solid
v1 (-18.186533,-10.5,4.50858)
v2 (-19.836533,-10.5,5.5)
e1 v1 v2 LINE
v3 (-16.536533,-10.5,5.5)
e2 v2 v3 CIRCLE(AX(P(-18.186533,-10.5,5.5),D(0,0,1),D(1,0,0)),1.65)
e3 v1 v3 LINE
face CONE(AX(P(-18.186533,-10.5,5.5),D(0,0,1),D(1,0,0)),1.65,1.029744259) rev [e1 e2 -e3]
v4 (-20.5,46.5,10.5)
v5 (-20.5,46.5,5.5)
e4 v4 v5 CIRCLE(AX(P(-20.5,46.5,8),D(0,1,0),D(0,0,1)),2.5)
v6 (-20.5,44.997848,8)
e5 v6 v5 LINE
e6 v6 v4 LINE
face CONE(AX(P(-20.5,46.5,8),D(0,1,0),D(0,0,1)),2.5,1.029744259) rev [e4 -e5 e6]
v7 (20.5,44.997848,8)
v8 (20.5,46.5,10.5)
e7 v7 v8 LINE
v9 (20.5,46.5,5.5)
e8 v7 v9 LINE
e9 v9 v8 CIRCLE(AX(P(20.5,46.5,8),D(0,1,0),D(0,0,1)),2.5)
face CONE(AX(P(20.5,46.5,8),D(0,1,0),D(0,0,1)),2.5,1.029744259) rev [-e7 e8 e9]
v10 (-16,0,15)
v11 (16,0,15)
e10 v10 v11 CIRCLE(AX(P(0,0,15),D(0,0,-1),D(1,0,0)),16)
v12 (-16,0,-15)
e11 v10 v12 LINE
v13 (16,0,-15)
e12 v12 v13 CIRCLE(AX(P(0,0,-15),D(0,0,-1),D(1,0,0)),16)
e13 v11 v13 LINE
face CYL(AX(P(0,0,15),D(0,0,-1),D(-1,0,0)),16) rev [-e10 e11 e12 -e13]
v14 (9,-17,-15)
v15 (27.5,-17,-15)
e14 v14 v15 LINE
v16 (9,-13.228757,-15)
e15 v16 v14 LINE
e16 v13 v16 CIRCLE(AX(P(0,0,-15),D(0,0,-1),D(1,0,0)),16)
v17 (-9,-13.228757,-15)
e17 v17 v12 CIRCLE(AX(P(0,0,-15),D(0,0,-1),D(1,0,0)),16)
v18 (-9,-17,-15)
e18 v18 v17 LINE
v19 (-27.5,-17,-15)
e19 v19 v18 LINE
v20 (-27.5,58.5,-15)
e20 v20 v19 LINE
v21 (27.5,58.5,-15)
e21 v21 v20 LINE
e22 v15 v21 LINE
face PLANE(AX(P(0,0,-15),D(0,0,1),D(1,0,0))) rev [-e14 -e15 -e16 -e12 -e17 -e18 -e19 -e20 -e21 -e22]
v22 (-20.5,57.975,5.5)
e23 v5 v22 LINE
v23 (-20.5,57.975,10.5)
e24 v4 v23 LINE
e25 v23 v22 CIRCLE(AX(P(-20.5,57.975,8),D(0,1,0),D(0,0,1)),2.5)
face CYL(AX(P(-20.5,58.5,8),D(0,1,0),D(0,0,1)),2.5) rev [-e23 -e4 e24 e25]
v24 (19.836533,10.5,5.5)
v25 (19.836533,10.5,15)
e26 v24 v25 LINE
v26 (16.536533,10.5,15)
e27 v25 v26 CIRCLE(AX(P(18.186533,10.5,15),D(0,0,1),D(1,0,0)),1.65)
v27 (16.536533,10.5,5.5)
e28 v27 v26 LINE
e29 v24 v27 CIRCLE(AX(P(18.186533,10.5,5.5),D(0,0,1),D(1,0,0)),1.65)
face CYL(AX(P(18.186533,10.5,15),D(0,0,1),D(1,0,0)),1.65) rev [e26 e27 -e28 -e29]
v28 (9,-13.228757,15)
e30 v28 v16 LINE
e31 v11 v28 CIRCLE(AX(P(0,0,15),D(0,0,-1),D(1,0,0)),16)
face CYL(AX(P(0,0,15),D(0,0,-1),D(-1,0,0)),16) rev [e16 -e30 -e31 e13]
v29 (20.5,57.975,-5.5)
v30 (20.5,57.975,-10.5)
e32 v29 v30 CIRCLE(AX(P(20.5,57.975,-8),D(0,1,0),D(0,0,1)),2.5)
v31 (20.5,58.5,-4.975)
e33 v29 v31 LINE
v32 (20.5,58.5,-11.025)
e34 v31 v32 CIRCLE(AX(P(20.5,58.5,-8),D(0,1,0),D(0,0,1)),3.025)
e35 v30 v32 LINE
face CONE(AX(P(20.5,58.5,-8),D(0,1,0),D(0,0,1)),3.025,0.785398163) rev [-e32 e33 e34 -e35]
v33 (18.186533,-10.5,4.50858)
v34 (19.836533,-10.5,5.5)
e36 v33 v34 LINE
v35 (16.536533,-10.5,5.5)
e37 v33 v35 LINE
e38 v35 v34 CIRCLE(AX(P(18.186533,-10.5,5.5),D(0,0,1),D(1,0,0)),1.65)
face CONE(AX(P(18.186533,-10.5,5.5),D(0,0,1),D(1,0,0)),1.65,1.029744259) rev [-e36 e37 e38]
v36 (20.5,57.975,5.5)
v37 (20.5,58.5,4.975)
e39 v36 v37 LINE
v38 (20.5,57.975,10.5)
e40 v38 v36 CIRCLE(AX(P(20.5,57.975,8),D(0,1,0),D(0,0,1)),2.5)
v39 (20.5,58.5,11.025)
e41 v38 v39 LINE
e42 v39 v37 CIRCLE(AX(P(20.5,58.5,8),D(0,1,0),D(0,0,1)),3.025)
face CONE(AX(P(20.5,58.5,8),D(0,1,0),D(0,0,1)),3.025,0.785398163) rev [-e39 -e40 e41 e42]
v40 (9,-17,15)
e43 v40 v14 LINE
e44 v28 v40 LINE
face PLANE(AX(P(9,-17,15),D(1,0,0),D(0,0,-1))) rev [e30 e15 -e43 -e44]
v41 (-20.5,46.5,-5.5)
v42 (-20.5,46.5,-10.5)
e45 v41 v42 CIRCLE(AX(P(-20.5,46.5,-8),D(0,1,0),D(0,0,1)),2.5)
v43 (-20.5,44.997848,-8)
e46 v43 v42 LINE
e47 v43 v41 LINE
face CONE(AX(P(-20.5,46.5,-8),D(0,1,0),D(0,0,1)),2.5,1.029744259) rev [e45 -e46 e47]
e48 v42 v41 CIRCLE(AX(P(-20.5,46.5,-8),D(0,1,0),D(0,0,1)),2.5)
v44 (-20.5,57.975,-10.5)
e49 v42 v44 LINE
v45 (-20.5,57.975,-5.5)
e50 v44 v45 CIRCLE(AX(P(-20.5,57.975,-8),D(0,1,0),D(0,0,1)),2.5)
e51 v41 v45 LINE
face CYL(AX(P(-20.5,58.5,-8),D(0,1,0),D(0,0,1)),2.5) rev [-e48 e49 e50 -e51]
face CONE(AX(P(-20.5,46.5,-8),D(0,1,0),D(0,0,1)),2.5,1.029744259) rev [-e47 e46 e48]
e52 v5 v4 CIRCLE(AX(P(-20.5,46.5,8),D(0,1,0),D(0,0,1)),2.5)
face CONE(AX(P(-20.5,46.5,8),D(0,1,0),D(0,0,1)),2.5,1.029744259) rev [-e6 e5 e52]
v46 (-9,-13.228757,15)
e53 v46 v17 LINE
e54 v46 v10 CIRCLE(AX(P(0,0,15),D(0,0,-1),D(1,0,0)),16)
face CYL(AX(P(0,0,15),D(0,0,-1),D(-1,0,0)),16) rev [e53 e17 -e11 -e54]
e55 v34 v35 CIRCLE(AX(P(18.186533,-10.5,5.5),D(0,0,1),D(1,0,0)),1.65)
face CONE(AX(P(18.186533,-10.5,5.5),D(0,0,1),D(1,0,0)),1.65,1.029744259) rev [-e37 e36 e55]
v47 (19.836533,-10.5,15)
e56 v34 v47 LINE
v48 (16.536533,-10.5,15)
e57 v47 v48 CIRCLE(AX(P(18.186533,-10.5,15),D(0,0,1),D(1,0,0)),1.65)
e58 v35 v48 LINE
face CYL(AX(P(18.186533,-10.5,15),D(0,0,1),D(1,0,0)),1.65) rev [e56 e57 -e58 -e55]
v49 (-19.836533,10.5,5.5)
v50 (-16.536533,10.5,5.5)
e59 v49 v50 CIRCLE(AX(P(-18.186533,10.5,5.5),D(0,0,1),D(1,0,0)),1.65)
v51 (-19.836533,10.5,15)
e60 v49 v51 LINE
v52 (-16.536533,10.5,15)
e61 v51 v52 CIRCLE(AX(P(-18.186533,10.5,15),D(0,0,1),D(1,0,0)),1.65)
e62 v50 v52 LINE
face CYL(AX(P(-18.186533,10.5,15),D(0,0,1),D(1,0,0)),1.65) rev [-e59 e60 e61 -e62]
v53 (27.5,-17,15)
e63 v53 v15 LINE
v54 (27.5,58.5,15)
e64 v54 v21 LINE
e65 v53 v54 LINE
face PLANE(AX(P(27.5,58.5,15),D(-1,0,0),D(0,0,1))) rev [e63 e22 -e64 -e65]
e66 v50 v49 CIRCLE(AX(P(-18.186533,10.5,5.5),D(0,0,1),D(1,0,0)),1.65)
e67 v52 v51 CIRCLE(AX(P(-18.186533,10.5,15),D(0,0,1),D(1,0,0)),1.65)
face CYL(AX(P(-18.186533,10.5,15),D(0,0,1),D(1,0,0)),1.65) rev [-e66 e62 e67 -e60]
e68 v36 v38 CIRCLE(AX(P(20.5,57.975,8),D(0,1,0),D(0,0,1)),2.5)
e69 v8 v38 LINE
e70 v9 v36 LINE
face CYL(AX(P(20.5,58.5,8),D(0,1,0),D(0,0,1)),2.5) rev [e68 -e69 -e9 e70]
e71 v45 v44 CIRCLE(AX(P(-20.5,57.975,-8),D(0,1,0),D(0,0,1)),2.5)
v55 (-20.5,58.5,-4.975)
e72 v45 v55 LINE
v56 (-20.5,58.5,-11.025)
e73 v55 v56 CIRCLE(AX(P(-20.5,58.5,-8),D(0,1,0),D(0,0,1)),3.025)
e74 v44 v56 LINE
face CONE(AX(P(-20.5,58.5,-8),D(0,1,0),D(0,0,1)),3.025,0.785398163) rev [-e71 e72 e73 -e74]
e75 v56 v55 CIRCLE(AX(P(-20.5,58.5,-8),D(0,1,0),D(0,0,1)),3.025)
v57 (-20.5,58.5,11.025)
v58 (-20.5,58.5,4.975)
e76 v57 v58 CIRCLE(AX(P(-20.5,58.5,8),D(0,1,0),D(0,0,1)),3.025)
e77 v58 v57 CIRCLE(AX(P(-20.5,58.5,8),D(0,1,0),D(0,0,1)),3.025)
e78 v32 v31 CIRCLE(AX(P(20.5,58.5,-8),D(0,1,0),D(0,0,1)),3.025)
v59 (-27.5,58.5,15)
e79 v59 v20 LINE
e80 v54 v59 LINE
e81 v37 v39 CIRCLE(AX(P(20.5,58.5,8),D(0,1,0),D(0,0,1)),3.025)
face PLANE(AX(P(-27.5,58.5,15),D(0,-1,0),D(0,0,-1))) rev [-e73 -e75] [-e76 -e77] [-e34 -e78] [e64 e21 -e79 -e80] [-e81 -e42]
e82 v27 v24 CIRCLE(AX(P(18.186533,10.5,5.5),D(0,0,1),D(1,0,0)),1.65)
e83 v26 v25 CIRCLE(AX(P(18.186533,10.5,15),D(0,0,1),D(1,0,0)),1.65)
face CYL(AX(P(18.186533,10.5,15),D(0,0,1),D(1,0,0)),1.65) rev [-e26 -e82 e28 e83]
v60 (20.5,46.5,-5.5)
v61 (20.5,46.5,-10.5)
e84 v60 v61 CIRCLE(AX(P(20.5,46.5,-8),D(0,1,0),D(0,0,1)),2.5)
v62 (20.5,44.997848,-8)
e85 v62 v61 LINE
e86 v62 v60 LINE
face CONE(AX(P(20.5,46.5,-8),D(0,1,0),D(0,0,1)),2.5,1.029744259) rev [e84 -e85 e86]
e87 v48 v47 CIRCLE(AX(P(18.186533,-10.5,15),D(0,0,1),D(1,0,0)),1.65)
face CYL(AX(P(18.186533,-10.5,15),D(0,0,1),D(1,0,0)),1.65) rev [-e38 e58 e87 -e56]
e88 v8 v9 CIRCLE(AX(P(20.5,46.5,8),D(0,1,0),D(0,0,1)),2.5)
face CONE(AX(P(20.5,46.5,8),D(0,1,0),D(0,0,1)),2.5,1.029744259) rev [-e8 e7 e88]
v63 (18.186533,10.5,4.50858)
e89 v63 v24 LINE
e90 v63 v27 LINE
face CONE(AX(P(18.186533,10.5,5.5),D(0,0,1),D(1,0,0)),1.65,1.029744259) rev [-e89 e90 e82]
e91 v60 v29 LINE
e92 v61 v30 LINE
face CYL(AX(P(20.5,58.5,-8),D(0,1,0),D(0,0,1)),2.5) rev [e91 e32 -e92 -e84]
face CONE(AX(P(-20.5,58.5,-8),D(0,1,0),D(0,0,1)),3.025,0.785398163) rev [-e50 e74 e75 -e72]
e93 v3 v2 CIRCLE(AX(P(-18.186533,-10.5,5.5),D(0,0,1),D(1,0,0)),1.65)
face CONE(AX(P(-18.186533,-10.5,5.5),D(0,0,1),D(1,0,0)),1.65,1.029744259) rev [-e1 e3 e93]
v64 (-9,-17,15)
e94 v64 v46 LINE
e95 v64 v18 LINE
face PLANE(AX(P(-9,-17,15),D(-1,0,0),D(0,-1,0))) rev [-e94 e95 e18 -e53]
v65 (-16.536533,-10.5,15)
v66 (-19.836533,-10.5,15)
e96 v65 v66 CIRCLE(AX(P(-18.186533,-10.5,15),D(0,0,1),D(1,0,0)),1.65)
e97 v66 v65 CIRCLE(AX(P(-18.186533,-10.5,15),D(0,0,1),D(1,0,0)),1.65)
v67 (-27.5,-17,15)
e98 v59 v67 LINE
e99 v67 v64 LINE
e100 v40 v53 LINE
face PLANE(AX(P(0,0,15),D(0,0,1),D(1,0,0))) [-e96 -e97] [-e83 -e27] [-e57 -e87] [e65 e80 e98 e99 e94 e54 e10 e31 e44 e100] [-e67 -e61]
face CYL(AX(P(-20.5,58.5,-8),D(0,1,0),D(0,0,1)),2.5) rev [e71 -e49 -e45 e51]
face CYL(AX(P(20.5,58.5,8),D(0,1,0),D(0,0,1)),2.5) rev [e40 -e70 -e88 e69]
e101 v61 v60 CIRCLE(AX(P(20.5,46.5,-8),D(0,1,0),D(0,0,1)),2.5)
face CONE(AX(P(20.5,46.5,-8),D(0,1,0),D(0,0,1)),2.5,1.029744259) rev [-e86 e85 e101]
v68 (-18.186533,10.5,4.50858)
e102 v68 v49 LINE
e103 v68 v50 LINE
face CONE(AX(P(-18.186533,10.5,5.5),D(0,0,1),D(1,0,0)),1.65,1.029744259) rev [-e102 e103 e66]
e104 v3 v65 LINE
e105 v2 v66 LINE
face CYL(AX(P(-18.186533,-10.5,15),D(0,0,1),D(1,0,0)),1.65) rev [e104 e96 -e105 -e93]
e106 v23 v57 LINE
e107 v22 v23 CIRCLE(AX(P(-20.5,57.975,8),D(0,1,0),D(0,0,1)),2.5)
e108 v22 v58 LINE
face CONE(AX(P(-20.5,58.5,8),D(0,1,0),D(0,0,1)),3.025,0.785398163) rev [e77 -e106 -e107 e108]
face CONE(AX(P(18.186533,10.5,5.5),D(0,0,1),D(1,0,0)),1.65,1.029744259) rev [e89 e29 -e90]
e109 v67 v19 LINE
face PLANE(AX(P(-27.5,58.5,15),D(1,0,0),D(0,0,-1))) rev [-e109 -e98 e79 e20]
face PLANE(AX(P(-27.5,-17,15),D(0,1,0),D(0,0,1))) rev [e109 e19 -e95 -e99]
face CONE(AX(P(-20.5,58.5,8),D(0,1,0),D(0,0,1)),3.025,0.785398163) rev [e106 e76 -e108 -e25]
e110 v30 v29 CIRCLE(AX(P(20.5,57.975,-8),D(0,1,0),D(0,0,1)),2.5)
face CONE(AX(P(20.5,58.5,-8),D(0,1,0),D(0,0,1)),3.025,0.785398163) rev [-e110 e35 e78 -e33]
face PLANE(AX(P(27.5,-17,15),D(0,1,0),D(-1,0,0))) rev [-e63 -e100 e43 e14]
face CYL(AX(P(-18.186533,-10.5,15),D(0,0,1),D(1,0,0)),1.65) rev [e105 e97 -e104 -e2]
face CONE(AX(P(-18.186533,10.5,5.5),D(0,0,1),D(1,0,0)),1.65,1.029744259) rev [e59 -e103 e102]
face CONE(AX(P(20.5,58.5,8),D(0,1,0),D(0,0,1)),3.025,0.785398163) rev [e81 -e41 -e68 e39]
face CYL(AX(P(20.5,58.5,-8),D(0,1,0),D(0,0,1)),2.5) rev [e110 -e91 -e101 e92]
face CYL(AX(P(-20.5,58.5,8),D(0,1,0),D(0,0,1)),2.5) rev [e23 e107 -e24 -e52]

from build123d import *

# Parameters (mm, degrees)
EXTRUDE_1_DEPTH              = 15
HOLE_WIZARD_M4_1_D           = 3.3
HOLE_WIZARD_M4_1_DEPTH       = 9.5
HOLE_WIZARD_M4_1_TIP         = 0.991420021
HOLE_WIZARD_M6_1_D           = 5
HOLE_WIZARD_M6_1_DEPTH       = 12
HOLE_WIZARD_M6_1_CSINK_D     = 6.05
HOLE_WIZARD_M6_1_CSINK_ANGLE = 90
HOLE_WIZARD_M6_1_TIP         = 1.502151548


with BuildPart() as part:
    # 草图1 → 凸台-拉伸1 (new, symmetric)
    with BuildSketch(Plane.XY):
        with BuildLine():
            Line((-27.5, 58.5), (27.5, 58.5))
            Line((27.5, 58.5), (27.5, -17))
            Line((27.5, -17), (9, -17))
            Line((9, -17), (9, -13.228756555))
            ThreePointArc((9, -13.228756555), (0, 16), (-9, -13.228756555))
            Line((-9, -13.228756555), (-9, -17))
            Line((-9, -17), (-27.5, -17))
            Line((-27.5, -17), (-27.5, 58.5))
        make_face()
    extrude(amount=EXTRUDE_1_DEPTH, both=True)

    # M4 螺纹孔1
    with Locations(Plane.XY.offset(15)):
        with Locations((18.186533479, 10.5), (18.186533479, -10.5), (-18.186533479, -10.5), (-18.186533479, 10.5)):
            Hole(HOLE_WIZARD_M4_1_D / 2, depth=HOLE_WIZARD_M4_1_DEPTH)
            with Locations((0, 0, -(HOLE_WIZARD_M4_1_DEPTH + HOLE_WIZARD_M4_1_TIP / 2))):  # 118° drill point
                Cone(0, HOLE_WIZARD_M4_1_D / 2, HOLE_WIZARD_M4_1_TIP, mode=Mode.SUBTRACT)

    # M6 螺纹孔1
    with Locations(Plane(origin=(-20.5, 58.5, 8), x_dir=(0, 0, 1), z_dir=(0, 1, 0))):
        with Locations((0, 0), (-16, 0), (-16, 41), (0, 41)):
            CounterSinkHole(HOLE_WIZARD_M6_1_D / 2, HOLE_WIZARD_M6_1_CSINK_D / 2, depth=HOLE_WIZARD_M6_1_DEPTH, counter_sink_angle=HOLE_WIZARD_M6_1_CSINK_ANGLE)
            with Locations((0, 0, -(HOLE_WIZARD_M6_1_DEPTH + HOLE_WIZARD_M6_1_TIP / 2))):  # 118° drill point
                Cone(0, HOLE_WIZARD_M6_1_D / 2, HOLE_WIZARD_M6_1_TIP, mode=Mode.SUBTRACT)


solid = part.part
